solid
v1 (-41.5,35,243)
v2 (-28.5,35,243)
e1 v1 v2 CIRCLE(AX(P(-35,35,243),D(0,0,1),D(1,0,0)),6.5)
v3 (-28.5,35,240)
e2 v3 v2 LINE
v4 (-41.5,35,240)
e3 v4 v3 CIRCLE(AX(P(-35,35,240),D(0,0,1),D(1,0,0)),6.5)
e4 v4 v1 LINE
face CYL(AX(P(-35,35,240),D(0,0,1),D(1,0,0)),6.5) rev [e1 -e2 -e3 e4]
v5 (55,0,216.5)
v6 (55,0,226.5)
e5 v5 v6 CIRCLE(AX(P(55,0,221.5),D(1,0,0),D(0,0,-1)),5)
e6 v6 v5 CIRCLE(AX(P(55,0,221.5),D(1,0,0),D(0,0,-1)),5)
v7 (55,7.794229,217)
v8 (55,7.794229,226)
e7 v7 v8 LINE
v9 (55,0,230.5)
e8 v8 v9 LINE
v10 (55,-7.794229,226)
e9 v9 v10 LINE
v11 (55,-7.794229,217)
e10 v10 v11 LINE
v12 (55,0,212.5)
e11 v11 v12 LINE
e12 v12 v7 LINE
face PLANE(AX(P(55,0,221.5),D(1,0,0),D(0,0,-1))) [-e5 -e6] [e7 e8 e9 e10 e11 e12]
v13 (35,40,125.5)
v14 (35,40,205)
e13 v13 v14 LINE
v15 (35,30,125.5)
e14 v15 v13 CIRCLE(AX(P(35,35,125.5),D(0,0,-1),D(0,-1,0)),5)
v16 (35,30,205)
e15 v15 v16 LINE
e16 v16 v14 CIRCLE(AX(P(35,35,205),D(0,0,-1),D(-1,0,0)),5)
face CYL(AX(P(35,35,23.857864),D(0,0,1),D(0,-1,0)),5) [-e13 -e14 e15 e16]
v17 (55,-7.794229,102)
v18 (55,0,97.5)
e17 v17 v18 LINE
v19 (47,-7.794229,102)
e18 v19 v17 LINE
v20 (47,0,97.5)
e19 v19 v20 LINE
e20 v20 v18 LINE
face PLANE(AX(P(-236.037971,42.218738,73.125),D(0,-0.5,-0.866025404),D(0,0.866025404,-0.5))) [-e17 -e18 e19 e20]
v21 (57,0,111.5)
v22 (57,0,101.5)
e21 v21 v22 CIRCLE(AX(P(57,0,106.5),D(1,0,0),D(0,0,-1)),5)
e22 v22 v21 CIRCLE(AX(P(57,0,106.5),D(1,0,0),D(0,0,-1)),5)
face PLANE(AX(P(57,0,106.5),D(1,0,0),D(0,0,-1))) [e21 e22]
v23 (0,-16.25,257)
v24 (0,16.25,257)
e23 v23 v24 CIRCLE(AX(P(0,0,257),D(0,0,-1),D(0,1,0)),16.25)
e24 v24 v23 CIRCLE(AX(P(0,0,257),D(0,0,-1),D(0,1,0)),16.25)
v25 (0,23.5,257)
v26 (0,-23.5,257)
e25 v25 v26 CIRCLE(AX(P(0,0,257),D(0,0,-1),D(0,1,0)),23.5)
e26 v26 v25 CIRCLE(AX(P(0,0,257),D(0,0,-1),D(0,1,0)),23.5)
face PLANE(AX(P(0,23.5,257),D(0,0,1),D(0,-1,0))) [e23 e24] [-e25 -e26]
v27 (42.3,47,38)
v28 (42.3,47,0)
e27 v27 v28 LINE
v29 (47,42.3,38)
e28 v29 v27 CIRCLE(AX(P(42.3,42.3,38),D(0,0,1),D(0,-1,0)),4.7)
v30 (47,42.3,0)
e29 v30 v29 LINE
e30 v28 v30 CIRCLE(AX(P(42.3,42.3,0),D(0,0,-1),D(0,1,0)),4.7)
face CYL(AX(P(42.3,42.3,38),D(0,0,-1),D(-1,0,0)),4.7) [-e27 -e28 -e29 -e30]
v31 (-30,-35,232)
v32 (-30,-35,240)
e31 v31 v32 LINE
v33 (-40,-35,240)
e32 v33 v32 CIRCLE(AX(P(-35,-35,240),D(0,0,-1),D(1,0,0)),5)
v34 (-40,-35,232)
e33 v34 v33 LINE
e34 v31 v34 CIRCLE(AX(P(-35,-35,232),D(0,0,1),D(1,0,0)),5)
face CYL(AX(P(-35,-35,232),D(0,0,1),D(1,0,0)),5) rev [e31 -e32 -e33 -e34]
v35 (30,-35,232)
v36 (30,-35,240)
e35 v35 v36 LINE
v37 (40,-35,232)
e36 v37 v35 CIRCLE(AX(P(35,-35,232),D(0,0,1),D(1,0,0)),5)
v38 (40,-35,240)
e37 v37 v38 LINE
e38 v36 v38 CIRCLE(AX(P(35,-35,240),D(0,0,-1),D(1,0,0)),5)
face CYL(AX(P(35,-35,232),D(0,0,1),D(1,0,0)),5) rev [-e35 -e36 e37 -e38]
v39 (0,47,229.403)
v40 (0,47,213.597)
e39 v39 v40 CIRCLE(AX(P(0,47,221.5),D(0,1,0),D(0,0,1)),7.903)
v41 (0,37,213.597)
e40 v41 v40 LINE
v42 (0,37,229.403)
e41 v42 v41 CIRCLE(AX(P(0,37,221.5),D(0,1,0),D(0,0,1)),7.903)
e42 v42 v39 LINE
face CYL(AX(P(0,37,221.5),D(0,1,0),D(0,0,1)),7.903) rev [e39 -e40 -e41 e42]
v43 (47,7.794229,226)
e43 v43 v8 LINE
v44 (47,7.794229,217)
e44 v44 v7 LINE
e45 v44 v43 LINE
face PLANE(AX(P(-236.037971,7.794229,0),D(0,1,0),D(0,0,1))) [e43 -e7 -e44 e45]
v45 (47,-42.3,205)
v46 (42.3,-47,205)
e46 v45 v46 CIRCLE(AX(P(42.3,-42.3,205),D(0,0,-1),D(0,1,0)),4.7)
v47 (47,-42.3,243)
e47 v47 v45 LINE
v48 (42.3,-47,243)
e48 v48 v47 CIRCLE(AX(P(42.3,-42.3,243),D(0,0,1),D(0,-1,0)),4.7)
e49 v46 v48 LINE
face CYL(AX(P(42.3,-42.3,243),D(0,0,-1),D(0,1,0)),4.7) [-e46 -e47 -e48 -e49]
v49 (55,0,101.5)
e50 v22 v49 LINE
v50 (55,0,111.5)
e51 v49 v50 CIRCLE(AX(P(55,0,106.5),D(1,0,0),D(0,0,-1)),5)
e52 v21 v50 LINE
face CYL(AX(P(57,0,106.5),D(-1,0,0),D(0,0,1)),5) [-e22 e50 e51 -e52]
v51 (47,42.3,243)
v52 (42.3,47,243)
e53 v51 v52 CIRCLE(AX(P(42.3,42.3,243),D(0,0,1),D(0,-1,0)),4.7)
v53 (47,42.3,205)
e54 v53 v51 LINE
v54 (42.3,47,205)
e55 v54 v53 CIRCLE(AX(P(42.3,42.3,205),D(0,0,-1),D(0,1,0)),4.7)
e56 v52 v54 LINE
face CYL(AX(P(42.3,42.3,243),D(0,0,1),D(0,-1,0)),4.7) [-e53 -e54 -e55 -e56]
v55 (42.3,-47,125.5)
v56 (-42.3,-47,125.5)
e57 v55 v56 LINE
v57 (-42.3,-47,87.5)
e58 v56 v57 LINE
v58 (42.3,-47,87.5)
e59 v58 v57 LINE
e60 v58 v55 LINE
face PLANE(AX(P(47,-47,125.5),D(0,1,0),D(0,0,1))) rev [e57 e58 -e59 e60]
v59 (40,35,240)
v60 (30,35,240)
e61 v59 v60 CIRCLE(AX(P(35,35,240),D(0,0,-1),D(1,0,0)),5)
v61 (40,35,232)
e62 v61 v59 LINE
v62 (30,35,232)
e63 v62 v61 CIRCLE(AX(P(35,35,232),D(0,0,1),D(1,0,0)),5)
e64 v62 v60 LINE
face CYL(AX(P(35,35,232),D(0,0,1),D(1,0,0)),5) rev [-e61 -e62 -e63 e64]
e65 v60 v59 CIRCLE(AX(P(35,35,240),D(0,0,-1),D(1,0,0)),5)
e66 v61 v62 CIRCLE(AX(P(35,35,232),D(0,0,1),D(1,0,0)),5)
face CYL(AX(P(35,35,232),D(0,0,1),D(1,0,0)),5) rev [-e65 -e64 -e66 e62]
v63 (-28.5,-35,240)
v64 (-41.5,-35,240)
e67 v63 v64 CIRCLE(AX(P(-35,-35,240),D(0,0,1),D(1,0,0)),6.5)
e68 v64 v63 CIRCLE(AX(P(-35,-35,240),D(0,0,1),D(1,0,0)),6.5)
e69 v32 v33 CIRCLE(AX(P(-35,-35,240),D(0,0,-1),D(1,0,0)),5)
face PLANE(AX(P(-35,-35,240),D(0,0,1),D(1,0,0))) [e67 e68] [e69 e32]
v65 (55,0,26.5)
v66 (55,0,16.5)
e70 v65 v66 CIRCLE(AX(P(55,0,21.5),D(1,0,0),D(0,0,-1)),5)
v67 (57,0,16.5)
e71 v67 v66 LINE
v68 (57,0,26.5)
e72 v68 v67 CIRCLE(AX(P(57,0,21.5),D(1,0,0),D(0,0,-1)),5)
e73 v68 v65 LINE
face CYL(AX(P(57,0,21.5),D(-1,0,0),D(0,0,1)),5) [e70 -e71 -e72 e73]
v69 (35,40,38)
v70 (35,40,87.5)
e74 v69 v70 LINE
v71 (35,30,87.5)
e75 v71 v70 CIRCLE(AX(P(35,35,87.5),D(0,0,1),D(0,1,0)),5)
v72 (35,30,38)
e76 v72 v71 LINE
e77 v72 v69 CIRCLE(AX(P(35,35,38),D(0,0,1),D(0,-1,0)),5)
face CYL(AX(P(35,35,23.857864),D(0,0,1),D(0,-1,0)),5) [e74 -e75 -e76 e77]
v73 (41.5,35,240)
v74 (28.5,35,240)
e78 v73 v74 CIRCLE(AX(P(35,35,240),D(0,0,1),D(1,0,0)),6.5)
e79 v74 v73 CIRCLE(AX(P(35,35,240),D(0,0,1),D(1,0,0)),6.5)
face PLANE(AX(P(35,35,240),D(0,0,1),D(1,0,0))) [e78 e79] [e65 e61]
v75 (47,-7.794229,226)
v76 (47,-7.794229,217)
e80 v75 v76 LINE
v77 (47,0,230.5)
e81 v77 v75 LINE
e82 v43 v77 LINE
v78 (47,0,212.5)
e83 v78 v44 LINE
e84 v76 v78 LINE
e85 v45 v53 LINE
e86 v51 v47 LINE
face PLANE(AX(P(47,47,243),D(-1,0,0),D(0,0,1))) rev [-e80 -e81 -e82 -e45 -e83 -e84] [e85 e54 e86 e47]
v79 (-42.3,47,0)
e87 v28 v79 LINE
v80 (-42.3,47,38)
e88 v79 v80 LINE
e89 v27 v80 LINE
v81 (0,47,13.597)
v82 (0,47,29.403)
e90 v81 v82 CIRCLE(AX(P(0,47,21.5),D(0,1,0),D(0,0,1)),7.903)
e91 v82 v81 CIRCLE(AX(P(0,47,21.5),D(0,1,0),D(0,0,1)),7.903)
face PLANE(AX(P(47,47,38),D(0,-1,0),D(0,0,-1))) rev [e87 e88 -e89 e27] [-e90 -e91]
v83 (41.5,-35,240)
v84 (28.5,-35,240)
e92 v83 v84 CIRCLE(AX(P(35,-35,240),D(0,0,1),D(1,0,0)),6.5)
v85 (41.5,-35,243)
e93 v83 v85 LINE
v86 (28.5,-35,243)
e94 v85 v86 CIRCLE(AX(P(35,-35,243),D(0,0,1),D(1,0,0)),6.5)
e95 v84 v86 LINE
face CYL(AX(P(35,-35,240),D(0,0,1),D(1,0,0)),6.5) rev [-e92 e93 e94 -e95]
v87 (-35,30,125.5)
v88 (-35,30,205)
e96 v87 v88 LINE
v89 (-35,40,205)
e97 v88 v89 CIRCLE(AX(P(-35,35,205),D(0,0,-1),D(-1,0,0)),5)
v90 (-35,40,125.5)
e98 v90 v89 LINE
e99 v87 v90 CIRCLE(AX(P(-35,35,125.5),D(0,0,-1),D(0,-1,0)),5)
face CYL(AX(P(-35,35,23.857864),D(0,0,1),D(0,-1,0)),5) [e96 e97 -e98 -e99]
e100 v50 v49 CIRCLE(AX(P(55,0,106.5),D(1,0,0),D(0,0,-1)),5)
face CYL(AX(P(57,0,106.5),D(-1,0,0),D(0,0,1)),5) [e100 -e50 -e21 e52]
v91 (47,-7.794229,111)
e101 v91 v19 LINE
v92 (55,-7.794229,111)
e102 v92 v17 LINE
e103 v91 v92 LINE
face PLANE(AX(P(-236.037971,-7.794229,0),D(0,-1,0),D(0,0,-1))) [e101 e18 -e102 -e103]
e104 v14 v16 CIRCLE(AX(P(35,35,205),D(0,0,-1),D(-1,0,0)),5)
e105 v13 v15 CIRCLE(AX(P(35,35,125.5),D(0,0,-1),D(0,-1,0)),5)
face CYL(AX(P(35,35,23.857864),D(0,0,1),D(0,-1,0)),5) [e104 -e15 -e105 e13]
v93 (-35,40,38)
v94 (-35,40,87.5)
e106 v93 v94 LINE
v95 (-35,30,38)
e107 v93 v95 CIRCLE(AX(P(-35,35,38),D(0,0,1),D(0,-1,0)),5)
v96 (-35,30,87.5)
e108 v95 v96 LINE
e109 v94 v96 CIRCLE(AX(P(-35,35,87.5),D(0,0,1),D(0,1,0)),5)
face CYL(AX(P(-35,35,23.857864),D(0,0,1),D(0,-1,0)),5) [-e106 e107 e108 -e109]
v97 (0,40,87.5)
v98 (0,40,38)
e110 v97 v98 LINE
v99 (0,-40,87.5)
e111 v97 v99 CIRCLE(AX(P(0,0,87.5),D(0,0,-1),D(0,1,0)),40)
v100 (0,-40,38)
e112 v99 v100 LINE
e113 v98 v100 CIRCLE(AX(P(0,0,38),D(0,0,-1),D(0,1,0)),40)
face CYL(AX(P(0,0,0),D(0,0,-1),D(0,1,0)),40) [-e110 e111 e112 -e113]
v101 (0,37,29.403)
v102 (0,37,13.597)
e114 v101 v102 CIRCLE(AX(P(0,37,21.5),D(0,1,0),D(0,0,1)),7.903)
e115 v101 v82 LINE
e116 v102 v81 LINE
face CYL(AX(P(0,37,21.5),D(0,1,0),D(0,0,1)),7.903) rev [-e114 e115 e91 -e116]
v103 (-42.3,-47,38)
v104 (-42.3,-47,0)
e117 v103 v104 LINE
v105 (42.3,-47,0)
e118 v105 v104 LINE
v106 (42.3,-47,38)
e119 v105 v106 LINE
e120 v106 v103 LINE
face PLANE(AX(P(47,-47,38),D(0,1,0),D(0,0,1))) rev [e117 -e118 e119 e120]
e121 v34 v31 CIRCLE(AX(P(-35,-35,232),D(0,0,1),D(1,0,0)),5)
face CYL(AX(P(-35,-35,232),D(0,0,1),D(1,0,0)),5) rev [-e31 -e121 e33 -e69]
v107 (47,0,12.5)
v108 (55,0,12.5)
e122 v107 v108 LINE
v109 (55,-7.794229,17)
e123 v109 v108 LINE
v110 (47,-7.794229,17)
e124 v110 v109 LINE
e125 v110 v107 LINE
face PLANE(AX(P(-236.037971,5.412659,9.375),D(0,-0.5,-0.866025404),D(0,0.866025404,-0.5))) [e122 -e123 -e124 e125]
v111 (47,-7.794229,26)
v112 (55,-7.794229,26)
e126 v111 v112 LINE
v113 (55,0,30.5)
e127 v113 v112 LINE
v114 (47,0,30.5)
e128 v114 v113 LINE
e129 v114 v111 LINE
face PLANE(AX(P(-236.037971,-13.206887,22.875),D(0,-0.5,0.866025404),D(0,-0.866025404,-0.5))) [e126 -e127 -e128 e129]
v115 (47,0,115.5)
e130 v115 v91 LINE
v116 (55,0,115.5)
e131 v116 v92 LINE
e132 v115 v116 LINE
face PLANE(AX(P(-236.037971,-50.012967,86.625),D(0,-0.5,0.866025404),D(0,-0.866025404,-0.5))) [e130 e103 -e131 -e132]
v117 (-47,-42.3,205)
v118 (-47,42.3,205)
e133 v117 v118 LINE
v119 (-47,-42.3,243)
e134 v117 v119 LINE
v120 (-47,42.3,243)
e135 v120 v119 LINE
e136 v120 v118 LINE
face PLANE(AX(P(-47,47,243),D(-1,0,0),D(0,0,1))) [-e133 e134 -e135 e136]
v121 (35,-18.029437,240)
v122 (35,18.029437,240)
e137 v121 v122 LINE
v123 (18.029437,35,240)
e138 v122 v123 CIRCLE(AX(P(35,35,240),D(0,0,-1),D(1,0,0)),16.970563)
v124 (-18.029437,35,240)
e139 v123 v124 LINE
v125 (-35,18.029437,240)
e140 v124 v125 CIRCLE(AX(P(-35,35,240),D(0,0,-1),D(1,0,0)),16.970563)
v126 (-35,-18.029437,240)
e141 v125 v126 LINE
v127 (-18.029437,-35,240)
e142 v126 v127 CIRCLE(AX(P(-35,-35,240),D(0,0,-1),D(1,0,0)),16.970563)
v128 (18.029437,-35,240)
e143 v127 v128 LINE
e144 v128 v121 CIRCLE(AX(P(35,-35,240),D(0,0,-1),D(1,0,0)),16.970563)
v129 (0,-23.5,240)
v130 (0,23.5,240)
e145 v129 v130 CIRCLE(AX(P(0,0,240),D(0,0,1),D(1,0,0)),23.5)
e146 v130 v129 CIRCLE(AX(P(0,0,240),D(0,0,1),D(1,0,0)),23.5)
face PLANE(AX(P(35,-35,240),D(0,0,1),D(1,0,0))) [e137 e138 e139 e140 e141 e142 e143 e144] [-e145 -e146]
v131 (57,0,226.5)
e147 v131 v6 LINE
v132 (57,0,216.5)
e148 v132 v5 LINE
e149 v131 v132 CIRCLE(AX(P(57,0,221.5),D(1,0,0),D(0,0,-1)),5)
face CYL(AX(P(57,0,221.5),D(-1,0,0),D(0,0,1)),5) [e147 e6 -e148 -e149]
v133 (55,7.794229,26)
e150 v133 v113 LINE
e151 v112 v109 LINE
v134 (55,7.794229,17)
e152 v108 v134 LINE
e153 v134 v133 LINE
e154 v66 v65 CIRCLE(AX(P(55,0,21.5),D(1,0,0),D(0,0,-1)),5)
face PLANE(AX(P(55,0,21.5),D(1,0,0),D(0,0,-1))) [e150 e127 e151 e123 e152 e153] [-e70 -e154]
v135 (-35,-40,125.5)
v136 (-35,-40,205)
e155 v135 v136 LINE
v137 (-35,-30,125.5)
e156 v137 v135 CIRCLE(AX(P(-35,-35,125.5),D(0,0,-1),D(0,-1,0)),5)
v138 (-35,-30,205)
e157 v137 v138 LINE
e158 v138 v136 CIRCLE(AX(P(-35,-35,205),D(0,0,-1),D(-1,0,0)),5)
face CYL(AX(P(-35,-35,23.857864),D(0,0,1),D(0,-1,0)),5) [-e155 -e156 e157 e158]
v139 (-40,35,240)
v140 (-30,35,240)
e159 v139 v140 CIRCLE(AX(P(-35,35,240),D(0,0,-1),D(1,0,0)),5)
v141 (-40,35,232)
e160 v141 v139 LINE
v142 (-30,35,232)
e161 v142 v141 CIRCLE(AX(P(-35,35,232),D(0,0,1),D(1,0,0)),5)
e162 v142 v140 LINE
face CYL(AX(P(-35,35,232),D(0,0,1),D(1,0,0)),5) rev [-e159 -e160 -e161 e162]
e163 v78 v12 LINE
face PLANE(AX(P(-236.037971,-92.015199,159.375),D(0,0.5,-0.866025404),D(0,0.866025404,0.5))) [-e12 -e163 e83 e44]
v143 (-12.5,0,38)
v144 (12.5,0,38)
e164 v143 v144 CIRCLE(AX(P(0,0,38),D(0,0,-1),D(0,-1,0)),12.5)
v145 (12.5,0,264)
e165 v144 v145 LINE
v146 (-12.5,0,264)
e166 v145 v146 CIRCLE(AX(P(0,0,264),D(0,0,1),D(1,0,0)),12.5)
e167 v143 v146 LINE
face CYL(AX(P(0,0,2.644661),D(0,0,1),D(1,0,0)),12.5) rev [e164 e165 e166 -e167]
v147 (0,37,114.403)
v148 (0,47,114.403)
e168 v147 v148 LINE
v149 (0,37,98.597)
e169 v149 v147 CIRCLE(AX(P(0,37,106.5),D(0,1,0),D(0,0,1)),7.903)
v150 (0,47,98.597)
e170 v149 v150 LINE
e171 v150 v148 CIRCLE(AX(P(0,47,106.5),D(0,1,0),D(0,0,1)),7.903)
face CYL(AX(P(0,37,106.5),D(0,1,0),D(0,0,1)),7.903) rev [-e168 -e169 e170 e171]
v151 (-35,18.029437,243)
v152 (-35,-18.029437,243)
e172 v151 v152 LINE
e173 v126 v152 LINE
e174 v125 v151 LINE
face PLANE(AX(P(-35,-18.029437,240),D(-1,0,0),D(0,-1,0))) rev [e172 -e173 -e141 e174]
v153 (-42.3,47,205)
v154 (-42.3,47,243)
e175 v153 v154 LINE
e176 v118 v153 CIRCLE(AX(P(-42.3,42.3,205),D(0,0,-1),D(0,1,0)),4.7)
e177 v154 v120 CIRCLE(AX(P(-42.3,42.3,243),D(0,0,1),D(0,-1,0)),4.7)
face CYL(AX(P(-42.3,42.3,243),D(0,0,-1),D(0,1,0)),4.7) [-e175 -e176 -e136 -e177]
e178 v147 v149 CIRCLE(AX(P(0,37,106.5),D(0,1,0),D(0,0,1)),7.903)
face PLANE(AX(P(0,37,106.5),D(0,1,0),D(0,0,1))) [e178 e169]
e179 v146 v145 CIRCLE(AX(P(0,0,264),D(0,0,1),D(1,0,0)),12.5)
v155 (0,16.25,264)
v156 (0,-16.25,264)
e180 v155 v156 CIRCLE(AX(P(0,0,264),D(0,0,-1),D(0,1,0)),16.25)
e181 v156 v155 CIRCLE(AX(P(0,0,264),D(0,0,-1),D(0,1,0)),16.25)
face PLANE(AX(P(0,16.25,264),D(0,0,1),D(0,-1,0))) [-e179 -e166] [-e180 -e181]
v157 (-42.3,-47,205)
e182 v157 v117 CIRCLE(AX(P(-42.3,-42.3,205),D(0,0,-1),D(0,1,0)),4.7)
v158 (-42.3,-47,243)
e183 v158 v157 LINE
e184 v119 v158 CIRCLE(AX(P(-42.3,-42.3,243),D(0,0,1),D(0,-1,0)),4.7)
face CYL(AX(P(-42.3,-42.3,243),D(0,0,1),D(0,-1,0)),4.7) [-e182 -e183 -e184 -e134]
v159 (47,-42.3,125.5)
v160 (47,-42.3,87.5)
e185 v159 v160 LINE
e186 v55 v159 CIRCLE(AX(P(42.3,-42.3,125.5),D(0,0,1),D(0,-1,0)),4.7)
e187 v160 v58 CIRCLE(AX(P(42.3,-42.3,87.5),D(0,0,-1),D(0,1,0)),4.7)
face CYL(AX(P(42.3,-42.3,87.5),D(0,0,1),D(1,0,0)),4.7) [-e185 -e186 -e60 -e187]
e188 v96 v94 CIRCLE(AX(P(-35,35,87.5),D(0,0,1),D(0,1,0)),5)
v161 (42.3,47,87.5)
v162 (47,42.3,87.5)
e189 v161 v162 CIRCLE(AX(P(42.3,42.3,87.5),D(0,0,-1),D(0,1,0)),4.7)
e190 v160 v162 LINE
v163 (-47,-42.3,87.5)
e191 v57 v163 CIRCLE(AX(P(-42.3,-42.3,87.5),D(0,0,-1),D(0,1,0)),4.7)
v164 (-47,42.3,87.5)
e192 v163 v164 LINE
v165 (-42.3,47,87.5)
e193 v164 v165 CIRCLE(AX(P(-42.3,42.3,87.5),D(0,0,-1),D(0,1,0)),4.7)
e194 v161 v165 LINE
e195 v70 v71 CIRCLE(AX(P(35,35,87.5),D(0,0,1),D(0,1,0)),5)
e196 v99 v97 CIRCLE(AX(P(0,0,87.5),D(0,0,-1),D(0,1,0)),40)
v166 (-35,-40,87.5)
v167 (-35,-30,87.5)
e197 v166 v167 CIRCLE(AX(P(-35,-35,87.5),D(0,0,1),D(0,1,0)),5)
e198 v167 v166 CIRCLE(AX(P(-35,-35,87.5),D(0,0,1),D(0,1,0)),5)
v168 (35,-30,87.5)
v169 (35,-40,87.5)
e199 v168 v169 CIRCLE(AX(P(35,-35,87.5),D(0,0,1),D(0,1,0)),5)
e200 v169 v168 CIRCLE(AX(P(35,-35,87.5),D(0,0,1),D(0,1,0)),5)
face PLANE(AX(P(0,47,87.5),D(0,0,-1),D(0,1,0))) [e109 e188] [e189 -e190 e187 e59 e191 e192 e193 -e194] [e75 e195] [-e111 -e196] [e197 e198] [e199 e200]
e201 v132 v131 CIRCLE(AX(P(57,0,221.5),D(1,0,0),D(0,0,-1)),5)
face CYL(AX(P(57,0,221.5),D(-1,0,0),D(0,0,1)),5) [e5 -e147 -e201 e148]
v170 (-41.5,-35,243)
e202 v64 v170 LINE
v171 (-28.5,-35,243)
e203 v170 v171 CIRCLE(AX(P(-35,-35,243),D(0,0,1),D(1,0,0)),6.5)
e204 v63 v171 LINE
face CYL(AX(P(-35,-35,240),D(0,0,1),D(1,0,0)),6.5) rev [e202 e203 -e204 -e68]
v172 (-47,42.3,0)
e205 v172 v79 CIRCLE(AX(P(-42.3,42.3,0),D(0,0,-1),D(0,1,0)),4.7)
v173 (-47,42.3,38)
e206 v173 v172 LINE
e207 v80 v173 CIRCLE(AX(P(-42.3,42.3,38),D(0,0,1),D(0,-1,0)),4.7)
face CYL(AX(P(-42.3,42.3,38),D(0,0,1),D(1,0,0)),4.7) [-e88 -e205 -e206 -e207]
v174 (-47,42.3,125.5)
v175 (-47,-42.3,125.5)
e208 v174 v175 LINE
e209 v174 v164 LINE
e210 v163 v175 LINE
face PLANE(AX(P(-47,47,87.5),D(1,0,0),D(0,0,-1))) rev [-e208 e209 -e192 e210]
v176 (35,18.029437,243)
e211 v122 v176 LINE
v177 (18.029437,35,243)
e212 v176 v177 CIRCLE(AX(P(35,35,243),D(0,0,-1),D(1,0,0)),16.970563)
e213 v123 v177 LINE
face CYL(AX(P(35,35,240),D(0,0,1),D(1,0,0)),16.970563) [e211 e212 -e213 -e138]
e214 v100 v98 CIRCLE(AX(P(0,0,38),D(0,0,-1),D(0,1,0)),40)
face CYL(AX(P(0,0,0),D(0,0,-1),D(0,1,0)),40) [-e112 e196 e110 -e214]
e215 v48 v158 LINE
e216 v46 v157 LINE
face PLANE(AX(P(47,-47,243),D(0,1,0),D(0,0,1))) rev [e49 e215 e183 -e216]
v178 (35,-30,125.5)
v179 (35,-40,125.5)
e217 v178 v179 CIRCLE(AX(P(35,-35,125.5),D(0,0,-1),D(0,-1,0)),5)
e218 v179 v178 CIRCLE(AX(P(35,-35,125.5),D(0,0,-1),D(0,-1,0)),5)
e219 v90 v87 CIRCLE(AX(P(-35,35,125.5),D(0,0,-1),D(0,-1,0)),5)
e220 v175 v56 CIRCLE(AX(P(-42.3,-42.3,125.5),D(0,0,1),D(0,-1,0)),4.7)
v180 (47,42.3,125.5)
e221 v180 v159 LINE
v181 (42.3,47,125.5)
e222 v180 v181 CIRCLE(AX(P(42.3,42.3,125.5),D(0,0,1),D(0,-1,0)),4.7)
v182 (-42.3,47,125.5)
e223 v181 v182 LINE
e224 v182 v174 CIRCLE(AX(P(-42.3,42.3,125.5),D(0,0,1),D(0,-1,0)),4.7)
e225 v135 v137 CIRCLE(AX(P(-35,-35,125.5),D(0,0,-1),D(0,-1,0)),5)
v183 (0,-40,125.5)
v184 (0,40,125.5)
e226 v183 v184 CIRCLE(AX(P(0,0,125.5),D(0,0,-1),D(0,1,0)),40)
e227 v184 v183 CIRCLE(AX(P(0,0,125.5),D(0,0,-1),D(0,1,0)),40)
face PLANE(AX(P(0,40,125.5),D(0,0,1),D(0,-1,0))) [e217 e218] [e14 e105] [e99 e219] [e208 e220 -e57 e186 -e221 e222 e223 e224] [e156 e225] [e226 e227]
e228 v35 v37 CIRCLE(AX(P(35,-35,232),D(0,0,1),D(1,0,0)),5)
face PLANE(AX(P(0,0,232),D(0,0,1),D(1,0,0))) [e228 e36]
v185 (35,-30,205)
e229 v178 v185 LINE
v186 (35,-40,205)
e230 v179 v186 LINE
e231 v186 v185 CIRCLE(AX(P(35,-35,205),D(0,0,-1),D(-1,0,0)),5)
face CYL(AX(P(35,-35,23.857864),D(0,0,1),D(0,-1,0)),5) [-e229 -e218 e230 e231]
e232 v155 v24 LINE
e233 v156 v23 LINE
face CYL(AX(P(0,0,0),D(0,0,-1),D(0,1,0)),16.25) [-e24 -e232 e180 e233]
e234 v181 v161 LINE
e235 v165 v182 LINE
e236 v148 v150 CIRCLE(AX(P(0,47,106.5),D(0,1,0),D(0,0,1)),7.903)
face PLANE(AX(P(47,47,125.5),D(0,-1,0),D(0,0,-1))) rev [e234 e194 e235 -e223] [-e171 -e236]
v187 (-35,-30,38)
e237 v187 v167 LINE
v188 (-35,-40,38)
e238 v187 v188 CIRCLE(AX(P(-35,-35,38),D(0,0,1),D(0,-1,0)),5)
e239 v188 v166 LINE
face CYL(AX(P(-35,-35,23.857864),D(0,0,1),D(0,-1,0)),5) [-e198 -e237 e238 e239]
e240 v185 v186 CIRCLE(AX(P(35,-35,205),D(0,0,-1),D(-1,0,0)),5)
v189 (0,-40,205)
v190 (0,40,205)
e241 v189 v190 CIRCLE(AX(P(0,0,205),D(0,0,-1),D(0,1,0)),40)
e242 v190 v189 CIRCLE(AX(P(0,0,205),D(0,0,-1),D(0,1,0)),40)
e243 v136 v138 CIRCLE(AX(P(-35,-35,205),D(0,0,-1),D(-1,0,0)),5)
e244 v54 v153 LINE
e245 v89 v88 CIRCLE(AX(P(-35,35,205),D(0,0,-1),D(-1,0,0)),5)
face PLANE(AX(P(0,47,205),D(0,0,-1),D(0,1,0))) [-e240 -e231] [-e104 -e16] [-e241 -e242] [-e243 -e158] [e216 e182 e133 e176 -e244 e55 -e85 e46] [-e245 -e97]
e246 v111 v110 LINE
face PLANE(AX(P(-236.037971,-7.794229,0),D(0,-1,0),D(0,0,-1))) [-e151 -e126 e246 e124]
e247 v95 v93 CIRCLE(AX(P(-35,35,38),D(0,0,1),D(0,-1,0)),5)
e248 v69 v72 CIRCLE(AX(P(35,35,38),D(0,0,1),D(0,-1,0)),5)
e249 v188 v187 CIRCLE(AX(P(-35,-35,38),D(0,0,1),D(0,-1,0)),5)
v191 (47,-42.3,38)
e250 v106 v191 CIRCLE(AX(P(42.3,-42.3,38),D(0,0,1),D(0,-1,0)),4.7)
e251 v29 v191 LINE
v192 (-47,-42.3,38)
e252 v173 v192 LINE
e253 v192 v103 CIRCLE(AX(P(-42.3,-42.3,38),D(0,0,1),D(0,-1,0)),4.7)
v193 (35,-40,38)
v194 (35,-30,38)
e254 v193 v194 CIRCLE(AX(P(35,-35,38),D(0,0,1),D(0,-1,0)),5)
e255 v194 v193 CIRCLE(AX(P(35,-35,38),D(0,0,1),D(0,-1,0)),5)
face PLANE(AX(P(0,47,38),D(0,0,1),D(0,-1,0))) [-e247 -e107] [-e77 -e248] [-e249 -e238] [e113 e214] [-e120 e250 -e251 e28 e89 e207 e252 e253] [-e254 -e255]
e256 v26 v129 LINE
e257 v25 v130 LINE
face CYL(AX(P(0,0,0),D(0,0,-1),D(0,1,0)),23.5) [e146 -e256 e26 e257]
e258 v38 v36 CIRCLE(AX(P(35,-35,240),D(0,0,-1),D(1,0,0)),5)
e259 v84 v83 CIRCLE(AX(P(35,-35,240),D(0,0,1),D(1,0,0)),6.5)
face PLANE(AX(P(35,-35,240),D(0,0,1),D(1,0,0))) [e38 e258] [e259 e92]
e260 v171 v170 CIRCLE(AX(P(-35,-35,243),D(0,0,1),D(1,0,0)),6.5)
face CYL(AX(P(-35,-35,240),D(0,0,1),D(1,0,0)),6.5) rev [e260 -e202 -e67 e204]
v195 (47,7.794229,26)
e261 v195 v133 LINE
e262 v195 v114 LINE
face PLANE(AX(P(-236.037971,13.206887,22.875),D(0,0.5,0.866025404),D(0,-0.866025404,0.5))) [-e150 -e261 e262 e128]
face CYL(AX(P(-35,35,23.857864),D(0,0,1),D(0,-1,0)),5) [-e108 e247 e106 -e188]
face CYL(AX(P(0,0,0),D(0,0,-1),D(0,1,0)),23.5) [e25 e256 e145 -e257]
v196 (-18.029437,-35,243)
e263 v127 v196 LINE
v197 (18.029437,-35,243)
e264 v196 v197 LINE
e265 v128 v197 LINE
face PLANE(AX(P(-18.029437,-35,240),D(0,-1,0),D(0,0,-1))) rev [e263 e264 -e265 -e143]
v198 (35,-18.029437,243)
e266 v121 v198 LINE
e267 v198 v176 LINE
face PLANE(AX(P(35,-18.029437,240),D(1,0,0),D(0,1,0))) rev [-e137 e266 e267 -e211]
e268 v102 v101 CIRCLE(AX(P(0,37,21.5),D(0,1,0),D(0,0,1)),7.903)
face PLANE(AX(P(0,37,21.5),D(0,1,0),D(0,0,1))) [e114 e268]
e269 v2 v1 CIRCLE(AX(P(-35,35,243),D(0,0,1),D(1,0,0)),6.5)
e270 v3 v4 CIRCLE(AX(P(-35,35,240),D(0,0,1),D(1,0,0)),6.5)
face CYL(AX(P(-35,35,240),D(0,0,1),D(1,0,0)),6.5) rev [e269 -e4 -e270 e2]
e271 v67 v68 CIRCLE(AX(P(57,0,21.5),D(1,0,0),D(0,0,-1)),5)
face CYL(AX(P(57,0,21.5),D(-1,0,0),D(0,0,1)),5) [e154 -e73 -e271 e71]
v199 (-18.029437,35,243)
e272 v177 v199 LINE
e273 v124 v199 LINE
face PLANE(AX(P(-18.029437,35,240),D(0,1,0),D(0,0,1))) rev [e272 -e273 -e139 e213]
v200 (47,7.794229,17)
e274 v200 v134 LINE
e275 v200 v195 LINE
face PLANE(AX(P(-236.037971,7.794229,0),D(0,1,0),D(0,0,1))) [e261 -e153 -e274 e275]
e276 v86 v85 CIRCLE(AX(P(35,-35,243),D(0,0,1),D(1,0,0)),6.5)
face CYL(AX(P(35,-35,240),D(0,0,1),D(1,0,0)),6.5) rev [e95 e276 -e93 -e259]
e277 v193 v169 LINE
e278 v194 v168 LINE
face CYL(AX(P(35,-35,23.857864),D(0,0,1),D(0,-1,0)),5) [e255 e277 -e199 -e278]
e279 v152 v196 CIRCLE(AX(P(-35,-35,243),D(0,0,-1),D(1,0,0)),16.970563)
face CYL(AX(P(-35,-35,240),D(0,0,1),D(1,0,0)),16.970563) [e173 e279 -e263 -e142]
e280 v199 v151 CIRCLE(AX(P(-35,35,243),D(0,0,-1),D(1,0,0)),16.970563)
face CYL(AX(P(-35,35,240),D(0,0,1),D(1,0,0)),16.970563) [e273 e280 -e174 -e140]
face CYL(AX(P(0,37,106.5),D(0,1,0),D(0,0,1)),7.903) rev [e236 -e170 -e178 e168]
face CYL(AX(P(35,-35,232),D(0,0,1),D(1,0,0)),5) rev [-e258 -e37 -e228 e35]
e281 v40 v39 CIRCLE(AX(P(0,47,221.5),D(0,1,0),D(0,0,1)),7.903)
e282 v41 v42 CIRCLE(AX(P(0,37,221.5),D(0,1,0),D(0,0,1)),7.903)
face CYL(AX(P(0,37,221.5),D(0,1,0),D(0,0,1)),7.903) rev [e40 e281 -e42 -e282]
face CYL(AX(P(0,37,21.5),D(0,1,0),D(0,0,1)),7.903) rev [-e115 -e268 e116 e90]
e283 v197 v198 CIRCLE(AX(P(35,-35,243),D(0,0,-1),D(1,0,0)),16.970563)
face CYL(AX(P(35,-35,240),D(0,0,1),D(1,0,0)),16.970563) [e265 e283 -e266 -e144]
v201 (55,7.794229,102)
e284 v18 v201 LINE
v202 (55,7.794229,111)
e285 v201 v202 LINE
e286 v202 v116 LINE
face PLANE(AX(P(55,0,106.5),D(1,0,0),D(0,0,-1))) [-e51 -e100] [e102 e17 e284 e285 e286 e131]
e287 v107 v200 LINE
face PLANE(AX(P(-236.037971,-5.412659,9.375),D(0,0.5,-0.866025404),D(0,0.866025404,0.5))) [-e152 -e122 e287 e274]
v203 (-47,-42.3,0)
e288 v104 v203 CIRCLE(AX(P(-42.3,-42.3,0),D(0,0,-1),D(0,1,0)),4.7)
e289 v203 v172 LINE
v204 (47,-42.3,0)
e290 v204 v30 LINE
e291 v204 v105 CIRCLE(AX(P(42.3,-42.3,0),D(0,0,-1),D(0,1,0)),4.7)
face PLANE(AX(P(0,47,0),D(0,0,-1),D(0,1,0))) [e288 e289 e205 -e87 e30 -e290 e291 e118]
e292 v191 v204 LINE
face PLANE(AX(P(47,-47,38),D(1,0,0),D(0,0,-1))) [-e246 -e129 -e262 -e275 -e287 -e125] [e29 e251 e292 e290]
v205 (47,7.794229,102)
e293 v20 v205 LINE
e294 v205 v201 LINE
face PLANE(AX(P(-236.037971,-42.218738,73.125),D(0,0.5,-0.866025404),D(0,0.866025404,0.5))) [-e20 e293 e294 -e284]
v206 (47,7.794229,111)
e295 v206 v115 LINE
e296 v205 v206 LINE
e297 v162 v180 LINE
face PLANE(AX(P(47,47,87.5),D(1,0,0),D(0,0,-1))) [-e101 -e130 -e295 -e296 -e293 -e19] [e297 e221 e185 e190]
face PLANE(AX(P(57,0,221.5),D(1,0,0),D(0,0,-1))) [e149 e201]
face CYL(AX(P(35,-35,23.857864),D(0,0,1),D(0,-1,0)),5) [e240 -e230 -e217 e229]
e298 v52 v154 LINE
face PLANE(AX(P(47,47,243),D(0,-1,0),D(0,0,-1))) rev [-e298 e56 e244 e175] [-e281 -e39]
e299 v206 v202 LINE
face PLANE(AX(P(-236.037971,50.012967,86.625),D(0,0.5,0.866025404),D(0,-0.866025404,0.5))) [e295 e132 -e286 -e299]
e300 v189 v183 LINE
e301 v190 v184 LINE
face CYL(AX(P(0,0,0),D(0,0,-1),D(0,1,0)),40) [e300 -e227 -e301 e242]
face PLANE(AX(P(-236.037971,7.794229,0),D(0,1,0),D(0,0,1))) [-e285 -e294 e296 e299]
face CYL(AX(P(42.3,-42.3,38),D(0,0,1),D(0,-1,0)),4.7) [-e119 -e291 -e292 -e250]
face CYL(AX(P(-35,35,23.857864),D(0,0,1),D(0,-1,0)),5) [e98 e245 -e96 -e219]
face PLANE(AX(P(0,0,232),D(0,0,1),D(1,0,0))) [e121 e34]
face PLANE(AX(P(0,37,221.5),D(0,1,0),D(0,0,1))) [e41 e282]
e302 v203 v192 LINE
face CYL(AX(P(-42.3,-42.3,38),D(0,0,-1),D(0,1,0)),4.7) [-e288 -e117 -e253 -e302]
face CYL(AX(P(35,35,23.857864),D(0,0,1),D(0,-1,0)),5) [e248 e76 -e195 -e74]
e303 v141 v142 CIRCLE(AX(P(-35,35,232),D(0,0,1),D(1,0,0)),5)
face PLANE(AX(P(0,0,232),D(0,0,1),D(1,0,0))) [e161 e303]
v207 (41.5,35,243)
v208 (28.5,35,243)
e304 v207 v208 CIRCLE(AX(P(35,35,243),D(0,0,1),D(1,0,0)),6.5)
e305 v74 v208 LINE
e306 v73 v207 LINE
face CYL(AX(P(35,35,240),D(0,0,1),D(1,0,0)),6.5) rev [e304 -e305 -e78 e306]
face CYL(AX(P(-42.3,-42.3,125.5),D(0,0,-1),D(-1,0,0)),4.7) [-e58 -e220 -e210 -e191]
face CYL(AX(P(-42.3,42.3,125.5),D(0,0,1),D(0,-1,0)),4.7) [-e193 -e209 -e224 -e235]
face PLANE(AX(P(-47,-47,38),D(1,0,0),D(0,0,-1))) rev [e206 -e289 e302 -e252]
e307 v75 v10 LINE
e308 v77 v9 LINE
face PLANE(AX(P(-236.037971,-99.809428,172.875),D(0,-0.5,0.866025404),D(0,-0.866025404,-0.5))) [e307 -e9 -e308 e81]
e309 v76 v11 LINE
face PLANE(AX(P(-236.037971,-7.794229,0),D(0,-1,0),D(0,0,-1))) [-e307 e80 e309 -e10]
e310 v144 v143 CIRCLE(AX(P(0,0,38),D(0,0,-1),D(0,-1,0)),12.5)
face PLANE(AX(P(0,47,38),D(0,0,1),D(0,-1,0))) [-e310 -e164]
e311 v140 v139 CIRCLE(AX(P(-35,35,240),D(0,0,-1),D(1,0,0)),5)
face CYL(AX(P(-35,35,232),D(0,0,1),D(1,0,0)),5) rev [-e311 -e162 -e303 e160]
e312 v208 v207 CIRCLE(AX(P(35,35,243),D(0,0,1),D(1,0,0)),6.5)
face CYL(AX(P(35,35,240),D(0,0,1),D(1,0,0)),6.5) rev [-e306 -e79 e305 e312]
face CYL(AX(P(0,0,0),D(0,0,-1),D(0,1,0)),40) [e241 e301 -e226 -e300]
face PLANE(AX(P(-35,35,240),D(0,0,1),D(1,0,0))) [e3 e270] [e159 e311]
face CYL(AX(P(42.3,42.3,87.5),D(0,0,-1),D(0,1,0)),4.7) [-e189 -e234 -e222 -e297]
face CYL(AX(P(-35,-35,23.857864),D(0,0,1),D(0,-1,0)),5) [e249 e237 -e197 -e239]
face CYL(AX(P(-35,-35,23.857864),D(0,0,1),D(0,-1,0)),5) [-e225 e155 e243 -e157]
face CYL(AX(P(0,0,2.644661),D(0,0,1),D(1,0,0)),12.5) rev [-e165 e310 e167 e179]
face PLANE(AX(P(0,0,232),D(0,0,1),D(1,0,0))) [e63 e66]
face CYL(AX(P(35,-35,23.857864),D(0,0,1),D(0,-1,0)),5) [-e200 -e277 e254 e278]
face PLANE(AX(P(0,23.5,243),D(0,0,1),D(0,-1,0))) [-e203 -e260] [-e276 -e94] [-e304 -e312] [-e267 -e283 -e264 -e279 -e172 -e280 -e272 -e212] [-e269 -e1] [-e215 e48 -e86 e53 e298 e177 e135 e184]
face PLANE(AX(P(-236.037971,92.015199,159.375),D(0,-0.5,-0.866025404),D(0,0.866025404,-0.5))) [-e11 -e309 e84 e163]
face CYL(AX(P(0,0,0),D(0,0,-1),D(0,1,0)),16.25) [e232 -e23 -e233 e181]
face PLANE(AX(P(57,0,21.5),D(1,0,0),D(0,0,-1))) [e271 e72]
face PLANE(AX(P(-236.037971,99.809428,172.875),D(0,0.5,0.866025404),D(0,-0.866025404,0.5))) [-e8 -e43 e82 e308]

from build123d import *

# Parameters (mm, degrees)
BOSS_EXTRUDE1_DEPTH      = 47
BOSS_EXTRUDE1_DEPTH_BACK = 47
SKETCH4_W                = 38
SKETCH4_H                = 94
BOSS_EXTRUDE2_REACH      = 217.506
SKETCH5_R                = 5
SKETCH6_R                = 5
CUT_EXTRUDE1_DEPTH       = 11
FILLET1_R                = 4.7
SKETCH9_R                = 9
BOSS_EXTRUDE3_DEPTH      = 8
SKETCH10_OUTSIDE_W       = 325.644
SKETCH10_OUTSIDE_H       = 155.644
CUT_EXTRUDE4_DEPTH       = 8
SKETCH11_R               = 5
BOSS_EXTRUDE5_DEPTH      = 2
SKETCH12_R               = 7.903
CUT_EXTRUDE5_DEPTH       = 10
SKETCH8_R                = 12.5
CUT_EXTRUDE6_DEPTH       = 226
CUT_EXTRUDE7_START       = -3
SKETCH13_R               = 6.5
SKETCH13_R_2             = 23.5
CUT_EXTRUDE7_DEPTH       = 3


with BuildPart() as part:
    # Sketch3 → Revolve1 (revolve)
    with BuildSketch(Plane(origin=(0, 0, 0), x_dir=(0, 0, -1), z_dir=(1, 0, 0))):
        Polygon((0, 0), (-264, 0), (-264, 16.25), (-257, 16.25), (-257, 23.5), (-243, 23.5), (-243, 47), (-205, 47), (-205, 40), (-125.5, 40), (-125.5, 47), (-87.5, 47), (-87.5, 40), (-38, 40), (-38, 47), (0, 47), align=None)
    revolve(axis=Axis((0, 0, 0), (0, 0, 1)))

    # Sketch4 → Boss-Extrude1 (add, two sides: drawn at the far end of the back side and taken through both)
    with BuildSketch(Plane(origin=(0, 0, 0), x_dir=(0, 0, -1), z_dir=(1, 0, 0)).offset(-BOSS_EXTRUDE1_DEPTH_BACK)):
        with Locations((-224, 0)):
            Rectangle(SKETCH4_W, SKETCH4_H)
        with Locations((-106.5, 0)):
            Rectangle(SKETCH4_W, SKETCH4_H)
        with Locations((-19, 0)):
            Rectangle(SKETCH4_W, SKETCH4_H)
    extrude(amount=BOSS_EXTRUDE1_DEPTH + BOSS_EXTRUDE1_DEPTH_BACK)

    # Sketch5 → Boss-Extrude2 (add, up to next)
    with BuildSketch(Plane(origin=(0, 0, 205), x_dir=(-1, 0, 0), z_dir=(0, 0, -1)), mode=Mode.PRIVATE) as boss_extrude2_sk1:
        with Locations(Location((-35, 35, 0), (0, 0, 270))):
            Circle(SKETCH5_R)
    boss_extrude2_tool1 = extrude(boss_extrude2_sk1.sketch, amount=BOSS_EXTRUDE2_REACH, mode=Mode.PRIVATE) - part.part
    # Sketch5 → Boss-Extrude2 (add, up to next)
    with BuildSketch(Plane(origin=(0, 0, 205), x_dir=(-1, 0, 0), z_dir=(0, 0, -1)), mode=Mode.PRIVATE) as boss_extrude2_sk2:
        with Locations(Location((35, 35, 0), (0, 0, 270))):
            Circle(SKETCH5_R)
    boss_extrude2_tool2 = extrude(boss_extrude2_sk2.sketch, amount=BOSS_EXTRUDE2_REACH, mode=Mode.PRIVATE) - part.part
    # Sketch5 → Boss-Extrude2 (add, up to next)
    with BuildSketch(Plane(origin=(0, 0, 205), x_dir=(-1, 0, 0), z_dir=(0, 0, -1)), mode=Mode.PRIVATE) as boss_extrude2_sk3:
        with Locations(Location((-35, -35, 0), (0, 0, 270))):
            Circle(SKETCH5_R)
    boss_extrude2_tool3 = extrude(boss_extrude2_sk3.sketch, amount=BOSS_EXTRUDE2_REACH, mode=Mode.PRIVATE) - part.part
    # Sketch5 → Boss-Extrude2 (add, up to next)
    with BuildSketch(Plane(origin=(0, 0, 205), x_dir=(-1, 0, 0), z_dir=(0, 0, -1)), mode=Mode.PRIVATE) as boss_extrude2_sk4:
        with Locations(Location((35, -35, 0), (0, 0, 270))):
            Circle(SKETCH5_R)
    boss_extrude2_tool4 = extrude(boss_extrude2_sk4.sketch, amount=BOSS_EXTRUDE2_REACH, mode=Mode.PRIVATE) - part.part
    add(boss_extrude2_tool1.solids().sort_by_distance((35, 35, 205))[0])
    add(boss_extrude2_tool1.solids().sort_by_distance((35, 35, 205))[1])
    add(boss_extrude2_tool2.solids().sort_by_distance((-35, 35, 205))[0])
    add(boss_extrude2_tool2.solids().sort_by_distance((-35, 35, 205))[1])
    add(boss_extrude2_tool3.solids().sort_by_distance((35, -35, 205))[0])
    add(boss_extrude2_tool3.solids().sort_by_distance((35, -35, 205))[1])
    add(boss_extrude2_tool4.solids().sort_by_distance((-35, -35, 205))[0])
    add(boss_extrude2_tool4.solids().sort_by_distance((-35, -35, 205))[1])

    # Sketch6 → Cut-Extrude1 (cut)
    with BuildSketch(Plane.XY.offset(243)):
        with Locations(Location((-35, 35, 0), (0, 0, 270))):
            Circle(SKETCH6_R)
        with Locations(Location((35, 35, 0), (0, 0, 270))):
            Circle(SKETCH6_R)
        with Locations(Location((-35, -35, 0), (0, 0, 270))):
            Circle(SKETCH6_R)
        with Locations(Location((35, -35, 0), (0, 0, 270))):
            Circle(SKETCH6_R)
    extrude(amount=-CUT_EXTRUDE1_DEPTH, mode=Mode.SUBTRACT)

    # Fillet1
    fillet1_edges = [part.edges().sort_by_distance(p)[0] for p in [
        (-47, -47, 224),
        (47, -47, 224),
        (-47, 47, 224),
        (47, 47, 224),
        (-47, -47, 106.5),
        (47, 47, 106.5),
        (-47, 47, 106.5),
        (47, -47, 106.5),
        (-47, -47, 19),
        (47, 47, 19),
        (-47, 47, 19),
        (47, -47, 19),
    ]]
    fillet(fillet1_edges, radius=FILLET1_R)

    # Sketch9 → Boss-Extrude3 (add)
    with BuildSketch(Plane(origin=(47, 0, 0), x_dir=(0, 0, -1), z_dir=(1, 0, 0))):
        with Locations(Location((-221.5, 0, 0), (0, 0, 180))):
            Circle(SKETCH9_R)
        with Locations((-106.5, 0)):
            Circle(SKETCH9_R)
        with Locations((-21.5, 0)):
            Circle(SKETCH9_R)
    extrude(amount=BOSS_EXTRUDE3_DEPTH)

    # Sketch10 outside → Cut-Extrude4 (cut)
    with BuildSketch(Plane(origin=(55, 0, 0), x_dir=(0, 0, -1), z_dir=(1, 0, 0))):
        with Locations((-132, 0)):
            Rectangle(SKETCH10_OUTSIDE_W, SKETCH10_OUTSIDE_H)
        Polygon((-217, -7.794228634), (-212.5, 0), (-217, 7.794228634), (-226, 7.794228634), (-230.5, 0), (-226, -7.794228634), align=None, mode=Mode.SUBTRACT)
        Polygon((-102, -7.794228634), (-97.5, 0), (-102, 7.794228634), (-111, 7.794228634), (-115.5, 0), (-111, -7.794228634), align=None, mode=Mode.SUBTRACT)
        Polygon((-17, -7.794228634), (-12.5, 0), (-17, 7.794228634), (-26, 7.794228634), (-30.5, 0), (-26, -7.794228634), align=None, mode=Mode.SUBTRACT)
    extrude(amount=-CUT_EXTRUDE4_DEPTH, mode=Mode.SUBTRACT)

    # Sketch11 → Boss-Extrude5 (add)
    with BuildSketch(Plane(origin=(55, 0, 0), x_dir=(0, 0, -1), z_dir=(1, 0, 0))):
        with Locations((-221.5, 0)):
            Circle(SKETCH11_R)
        with Locations((-106.5, 0)):
            Circle(SKETCH11_R)
        with Locations((-21.5, 0)):
            Circle(SKETCH11_R)
    extrude(amount=BOSS_EXTRUDE5_DEPTH)

    # Sketch12 → Cut-Extrude5 (cut)
    with BuildSketch(Plane(origin=(0, 47, 0), x_dir=(1, 0, 0), z_dir=(0, 1, 0))):
        with Locations(Location((0, -221.5, 0), (0, 0, 270))):
            Circle(SKETCH12_R)
        with Locations(Location((0, -106.5, 0), (0, 0, 270))):
            Circle(SKETCH12_R)
        with Locations(Location((0, -21.5, 0), (0, 0, 270))):
            Circle(SKETCH12_R)
    extrude(amount=-CUT_EXTRUDE5_DEPTH, mode=Mode.SUBTRACT)

    # Sketch8 → Cut-Extrude6 (cut)
    with BuildSketch(Plane.XY.offset(264)):
        Circle(SKETCH8_R)
    extrude(amount=-CUT_EXTRUDE6_DEPTH, mode=Mode.SUBTRACT)

    # Sketch13 → Cut-Extrude7 (cut)
    # profile 1 of 5: a face of its own
    with BuildSketch(Plane.XY.offset(243).offset(CUT_EXTRUDE7_START)):
        with Locations((-35, 35)):
            Circle(SKETCH13_R)
    # profile 2 of 5: a face of its own
    with BuildSketch(Plane.XY.offset(243).offset(CUT_EXTRUDE7_START)):
        with Locations((35, 35)):
            Circle(SKETCH13_R)
    # profile 3 of 5: a face of its own
    with BuildSketch(Plane.XY.offset(243).offset(CUT_EXTRUDE7_START)):
        with Locations((35, -35)):
            Circle(SKETCH13_R)
    # profile 4 of 5: a face of its own
    with BuildSketch(Plane.XY.offset(243).offset(CUT_EXTRUDE7_START)):
        with Locations((-35, -35)):
            Circle(SKETCH13_R)
    # profile 5 of 5: a face of its own
    with BuildSketch(Plane.XY.offset(243).offset(CUT_EXTRUDE7_START)):
        with BuildLine():
            Line((-35, -18.029437252), (-35, 18.029437252))
            ThreePointArc((-35, 18.029437252), (-23, 23), (-18.029437252, 35))
            Line((-18.029437252, 35), (18.029437252, 35))
            ThreePointArc((18.029437252, 35), (23, 23), (35, 18.029437252))
            Line((35, 18.029437252), (35, -18.029437252))
            ThreePointArc((35, -18.029437252), (23, -23), (18.029437252, -35))
            Line((18.029437252, -35), (-18.029437252, -35))
            ThreePointArc((-18.029437252, -35), (-23, -23), (-35, -18.029437252))
        make_face()
        with Locations(Location((0, 0, 0), (0, 0, 90))):
            Circle(SKETCH13_R_2, mode=Mode.SUBTRACT)
    extrude(amount=CUT_EXTRUDE7_DEPTH, mode=Mode.SUBTRACT)


solid = part.part
